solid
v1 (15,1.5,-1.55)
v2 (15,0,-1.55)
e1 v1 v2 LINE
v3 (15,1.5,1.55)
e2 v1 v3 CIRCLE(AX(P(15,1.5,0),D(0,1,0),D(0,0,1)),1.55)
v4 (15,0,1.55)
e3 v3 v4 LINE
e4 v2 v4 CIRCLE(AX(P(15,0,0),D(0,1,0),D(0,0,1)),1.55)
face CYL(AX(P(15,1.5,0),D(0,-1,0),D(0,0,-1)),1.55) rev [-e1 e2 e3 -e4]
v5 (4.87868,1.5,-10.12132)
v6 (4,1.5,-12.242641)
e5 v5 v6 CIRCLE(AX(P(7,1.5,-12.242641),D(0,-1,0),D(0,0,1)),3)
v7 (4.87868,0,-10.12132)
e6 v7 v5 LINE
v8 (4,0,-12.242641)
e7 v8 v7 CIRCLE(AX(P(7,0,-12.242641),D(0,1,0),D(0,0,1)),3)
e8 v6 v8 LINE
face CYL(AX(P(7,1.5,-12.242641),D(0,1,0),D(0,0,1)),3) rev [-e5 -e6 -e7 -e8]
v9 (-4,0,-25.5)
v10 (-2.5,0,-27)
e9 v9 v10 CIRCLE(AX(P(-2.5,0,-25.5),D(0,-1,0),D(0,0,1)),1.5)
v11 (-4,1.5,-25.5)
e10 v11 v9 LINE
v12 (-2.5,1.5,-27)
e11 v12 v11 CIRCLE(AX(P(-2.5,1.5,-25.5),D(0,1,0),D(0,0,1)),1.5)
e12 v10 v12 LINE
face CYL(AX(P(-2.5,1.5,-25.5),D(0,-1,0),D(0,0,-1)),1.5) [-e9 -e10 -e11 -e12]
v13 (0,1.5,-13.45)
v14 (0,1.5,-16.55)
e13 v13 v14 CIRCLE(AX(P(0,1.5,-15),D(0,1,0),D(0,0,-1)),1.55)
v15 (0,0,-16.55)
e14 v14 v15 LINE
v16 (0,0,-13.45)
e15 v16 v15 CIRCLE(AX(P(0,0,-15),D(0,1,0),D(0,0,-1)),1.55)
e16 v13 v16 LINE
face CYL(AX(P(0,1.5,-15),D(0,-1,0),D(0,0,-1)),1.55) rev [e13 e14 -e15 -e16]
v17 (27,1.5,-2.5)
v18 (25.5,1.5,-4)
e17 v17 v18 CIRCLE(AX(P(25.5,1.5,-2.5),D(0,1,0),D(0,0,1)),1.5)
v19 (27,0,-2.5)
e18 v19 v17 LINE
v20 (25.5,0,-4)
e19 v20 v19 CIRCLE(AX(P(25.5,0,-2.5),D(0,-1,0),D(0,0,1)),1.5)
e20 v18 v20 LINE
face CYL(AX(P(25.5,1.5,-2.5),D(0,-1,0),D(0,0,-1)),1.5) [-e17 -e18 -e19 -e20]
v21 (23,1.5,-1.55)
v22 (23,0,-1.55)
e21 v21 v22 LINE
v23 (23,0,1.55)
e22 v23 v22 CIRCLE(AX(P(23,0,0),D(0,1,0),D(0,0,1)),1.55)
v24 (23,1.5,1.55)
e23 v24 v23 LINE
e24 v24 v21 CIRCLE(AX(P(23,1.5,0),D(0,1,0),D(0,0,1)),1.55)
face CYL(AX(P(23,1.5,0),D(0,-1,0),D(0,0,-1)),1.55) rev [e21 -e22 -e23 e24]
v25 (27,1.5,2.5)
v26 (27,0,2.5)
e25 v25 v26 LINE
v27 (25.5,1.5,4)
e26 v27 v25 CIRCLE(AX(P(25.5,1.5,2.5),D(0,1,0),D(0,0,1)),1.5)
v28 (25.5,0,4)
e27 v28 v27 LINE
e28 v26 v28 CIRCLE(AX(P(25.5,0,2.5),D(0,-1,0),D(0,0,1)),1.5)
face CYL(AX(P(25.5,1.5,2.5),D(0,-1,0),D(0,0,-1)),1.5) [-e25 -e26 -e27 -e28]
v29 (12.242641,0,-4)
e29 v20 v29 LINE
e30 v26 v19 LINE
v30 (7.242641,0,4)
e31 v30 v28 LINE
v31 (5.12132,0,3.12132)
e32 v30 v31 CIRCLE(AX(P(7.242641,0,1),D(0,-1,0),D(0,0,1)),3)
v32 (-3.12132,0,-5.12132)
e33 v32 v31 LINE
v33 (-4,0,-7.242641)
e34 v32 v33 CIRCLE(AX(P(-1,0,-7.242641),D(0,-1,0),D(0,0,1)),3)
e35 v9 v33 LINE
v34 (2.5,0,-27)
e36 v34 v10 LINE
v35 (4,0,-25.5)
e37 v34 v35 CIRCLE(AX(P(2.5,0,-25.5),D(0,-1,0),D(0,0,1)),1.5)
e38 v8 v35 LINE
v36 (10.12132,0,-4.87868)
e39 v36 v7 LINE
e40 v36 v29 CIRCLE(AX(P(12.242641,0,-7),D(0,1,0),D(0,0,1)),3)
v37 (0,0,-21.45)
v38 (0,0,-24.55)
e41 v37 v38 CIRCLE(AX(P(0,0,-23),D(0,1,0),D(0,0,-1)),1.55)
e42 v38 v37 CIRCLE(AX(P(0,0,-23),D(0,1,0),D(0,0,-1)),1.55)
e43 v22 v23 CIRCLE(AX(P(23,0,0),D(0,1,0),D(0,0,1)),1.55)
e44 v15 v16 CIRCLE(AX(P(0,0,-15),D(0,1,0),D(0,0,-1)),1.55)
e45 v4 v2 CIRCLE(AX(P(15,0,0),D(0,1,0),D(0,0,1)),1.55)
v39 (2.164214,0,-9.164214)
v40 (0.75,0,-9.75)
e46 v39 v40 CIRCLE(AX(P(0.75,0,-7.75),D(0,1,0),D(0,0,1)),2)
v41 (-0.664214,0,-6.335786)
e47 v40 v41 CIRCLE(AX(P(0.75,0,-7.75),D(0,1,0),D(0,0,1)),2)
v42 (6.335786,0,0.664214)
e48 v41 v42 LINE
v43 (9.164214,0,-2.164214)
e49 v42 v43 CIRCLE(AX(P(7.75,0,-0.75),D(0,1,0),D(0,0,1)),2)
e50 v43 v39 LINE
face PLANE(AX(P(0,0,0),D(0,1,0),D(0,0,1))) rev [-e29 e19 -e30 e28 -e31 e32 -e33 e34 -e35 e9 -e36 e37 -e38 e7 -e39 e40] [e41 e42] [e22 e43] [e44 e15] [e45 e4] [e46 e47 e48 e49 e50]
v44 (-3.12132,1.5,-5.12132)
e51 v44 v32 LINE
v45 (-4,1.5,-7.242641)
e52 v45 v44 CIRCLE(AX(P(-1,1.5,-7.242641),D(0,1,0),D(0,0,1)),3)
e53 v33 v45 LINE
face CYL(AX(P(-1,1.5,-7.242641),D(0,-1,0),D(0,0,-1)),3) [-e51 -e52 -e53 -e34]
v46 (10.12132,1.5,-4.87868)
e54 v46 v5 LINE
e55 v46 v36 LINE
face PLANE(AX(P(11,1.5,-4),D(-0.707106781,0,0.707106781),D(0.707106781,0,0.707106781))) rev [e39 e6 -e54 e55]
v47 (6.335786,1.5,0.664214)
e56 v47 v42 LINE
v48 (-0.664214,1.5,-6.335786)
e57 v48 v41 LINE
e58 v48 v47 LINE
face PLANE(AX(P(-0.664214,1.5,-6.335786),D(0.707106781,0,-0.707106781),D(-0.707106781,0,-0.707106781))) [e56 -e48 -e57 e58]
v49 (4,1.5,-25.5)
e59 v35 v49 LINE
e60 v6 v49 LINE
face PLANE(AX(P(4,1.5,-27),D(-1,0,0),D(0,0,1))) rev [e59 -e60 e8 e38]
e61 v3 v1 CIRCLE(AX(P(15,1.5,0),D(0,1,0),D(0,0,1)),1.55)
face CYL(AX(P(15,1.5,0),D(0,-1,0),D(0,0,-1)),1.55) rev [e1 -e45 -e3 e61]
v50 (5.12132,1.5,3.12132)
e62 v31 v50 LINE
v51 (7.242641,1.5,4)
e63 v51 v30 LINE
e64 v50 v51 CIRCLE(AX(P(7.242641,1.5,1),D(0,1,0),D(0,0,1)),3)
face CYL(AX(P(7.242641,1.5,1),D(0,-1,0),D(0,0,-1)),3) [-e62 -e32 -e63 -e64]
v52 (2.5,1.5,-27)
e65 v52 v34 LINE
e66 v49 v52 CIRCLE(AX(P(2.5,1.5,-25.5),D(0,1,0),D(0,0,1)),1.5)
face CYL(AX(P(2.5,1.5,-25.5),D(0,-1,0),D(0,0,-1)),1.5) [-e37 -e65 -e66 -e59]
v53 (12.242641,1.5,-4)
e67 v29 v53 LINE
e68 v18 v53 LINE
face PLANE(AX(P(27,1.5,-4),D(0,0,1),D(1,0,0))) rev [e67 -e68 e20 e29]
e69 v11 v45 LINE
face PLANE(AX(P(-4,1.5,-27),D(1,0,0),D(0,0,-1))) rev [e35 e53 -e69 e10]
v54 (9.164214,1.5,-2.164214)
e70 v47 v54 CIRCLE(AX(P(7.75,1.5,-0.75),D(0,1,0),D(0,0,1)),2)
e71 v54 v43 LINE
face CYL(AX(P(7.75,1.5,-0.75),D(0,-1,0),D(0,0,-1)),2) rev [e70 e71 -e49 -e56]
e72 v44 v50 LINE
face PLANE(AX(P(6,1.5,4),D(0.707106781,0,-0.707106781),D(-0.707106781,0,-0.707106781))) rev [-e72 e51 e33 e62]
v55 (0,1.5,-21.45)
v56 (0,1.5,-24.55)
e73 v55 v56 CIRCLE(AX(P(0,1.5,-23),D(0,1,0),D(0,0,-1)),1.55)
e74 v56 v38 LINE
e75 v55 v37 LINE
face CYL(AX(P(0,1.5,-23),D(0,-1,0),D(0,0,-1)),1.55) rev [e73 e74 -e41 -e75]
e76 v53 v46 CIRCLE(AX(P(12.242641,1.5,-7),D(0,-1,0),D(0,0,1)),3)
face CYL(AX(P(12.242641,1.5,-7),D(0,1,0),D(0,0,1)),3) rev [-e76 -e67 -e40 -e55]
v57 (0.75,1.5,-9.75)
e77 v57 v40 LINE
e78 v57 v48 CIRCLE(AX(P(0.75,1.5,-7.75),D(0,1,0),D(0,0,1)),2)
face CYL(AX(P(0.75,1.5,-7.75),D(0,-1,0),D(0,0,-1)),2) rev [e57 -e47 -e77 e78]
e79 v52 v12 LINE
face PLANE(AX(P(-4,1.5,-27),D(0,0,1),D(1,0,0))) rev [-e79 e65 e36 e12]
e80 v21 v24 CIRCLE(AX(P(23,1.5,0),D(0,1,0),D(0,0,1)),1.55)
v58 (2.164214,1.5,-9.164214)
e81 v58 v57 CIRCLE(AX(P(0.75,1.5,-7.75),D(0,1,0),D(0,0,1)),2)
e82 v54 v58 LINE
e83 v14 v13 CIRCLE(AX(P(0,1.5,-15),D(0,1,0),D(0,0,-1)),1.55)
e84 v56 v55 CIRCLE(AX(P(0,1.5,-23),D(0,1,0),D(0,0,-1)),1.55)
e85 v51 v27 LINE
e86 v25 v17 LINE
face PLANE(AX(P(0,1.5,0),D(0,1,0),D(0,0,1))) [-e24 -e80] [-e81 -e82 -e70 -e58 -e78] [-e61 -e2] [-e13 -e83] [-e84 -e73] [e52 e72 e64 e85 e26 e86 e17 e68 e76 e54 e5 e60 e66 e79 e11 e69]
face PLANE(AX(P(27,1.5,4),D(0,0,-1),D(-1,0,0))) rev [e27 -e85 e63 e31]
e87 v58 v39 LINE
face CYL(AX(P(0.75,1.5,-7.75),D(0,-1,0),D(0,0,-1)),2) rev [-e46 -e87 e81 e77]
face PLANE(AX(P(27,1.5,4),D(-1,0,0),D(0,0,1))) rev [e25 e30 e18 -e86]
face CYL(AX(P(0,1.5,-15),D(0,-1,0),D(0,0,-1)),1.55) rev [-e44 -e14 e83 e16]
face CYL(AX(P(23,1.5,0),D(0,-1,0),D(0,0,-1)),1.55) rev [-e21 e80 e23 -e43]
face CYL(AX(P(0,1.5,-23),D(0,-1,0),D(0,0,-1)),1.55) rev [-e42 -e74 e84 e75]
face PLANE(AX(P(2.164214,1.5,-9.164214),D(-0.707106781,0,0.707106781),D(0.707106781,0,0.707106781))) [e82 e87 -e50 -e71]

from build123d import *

# Parameters (mm, degrees)
SKETCH_1_R      = 1.55
EXTRUDE_1_DEPTH = 1.5
FILLET_1_R      = 1.5
FILLET_2_R      = 3


with BuildPart() as part:
    # 草图1 → 凸台-拉伸1 (new body)
    with BuildSketch(Plane(origin=(0, 0, 0), x_dir=(1, 0, 0), z_dir=(0, 1, 0))):
        Polygon((27, -4), (27, 4), (11, 4), (4, 11), (4, 27), (-4, 27), (-4, 6), (6, -4), align=None)
        with Locations(Location((15, 0, 0), (0, 0, 270))):
            Circle(SKETCH_1_R, mode=Mode.SUBTRACT)
        with Locations(Location((23, 0, 0), (0, 0, 270))):
            Circle(SKETCH_1_R, mode=Mode.SUBTRACT)
        with Locations(Location((0, 23, 0), (0, 0, 90))):
            Circle(SKETCH_1_R, mode=Mode.SUBTRACT)
        with Locations(Location((0, 15, 0), (0, 0, 90))):
            Circle(SKETCH_1_R, mode=Mode.SUBTRACT)
        with BuildLine():
            Line((2.164213562, 9.164213562), (9.164213562, 2.164213562))
            ThreePointArc((9.164213562, 2.164213562), (9.164213562, -0.664213562), (6.335786438, -0.664213562))
            Line((6.335786438, -0.664213562), (-0.664213562, 6.335786438))
            ThreePointArc((-0.664213562, 6.335786438), (-0.664213562, 9.164213562), (2.164213562, 9.164213562))
        make_face(mode=Mode.SUBTRACT)
    extrude(amount=EXTRUDE_1_DEPTH)

    # 圆角1
    fillet_1_edges = [part.edges().sort_by_distance(p)[0] for p in [
        (-4, 0.75, -27),
        (4, 0.75, -27),
        (27, 0.75, -4),
        (27, 0.75, 4),
    ]]
    fillet(fillet_1_edges, radius=FILLET_1_R)

    # 圆角2
    fillet_2_edges = [part.edges().sort_by_distance(p)[0] for p in [
        (6, 0.75, 4),
        (-4, 0.75, -6),
        (4, 0.75, -11),
        (11, 0.75, -4),
    ]]
    fillet(fillet_2_edges, radius=FILLET_2_R)


solid = part.part
